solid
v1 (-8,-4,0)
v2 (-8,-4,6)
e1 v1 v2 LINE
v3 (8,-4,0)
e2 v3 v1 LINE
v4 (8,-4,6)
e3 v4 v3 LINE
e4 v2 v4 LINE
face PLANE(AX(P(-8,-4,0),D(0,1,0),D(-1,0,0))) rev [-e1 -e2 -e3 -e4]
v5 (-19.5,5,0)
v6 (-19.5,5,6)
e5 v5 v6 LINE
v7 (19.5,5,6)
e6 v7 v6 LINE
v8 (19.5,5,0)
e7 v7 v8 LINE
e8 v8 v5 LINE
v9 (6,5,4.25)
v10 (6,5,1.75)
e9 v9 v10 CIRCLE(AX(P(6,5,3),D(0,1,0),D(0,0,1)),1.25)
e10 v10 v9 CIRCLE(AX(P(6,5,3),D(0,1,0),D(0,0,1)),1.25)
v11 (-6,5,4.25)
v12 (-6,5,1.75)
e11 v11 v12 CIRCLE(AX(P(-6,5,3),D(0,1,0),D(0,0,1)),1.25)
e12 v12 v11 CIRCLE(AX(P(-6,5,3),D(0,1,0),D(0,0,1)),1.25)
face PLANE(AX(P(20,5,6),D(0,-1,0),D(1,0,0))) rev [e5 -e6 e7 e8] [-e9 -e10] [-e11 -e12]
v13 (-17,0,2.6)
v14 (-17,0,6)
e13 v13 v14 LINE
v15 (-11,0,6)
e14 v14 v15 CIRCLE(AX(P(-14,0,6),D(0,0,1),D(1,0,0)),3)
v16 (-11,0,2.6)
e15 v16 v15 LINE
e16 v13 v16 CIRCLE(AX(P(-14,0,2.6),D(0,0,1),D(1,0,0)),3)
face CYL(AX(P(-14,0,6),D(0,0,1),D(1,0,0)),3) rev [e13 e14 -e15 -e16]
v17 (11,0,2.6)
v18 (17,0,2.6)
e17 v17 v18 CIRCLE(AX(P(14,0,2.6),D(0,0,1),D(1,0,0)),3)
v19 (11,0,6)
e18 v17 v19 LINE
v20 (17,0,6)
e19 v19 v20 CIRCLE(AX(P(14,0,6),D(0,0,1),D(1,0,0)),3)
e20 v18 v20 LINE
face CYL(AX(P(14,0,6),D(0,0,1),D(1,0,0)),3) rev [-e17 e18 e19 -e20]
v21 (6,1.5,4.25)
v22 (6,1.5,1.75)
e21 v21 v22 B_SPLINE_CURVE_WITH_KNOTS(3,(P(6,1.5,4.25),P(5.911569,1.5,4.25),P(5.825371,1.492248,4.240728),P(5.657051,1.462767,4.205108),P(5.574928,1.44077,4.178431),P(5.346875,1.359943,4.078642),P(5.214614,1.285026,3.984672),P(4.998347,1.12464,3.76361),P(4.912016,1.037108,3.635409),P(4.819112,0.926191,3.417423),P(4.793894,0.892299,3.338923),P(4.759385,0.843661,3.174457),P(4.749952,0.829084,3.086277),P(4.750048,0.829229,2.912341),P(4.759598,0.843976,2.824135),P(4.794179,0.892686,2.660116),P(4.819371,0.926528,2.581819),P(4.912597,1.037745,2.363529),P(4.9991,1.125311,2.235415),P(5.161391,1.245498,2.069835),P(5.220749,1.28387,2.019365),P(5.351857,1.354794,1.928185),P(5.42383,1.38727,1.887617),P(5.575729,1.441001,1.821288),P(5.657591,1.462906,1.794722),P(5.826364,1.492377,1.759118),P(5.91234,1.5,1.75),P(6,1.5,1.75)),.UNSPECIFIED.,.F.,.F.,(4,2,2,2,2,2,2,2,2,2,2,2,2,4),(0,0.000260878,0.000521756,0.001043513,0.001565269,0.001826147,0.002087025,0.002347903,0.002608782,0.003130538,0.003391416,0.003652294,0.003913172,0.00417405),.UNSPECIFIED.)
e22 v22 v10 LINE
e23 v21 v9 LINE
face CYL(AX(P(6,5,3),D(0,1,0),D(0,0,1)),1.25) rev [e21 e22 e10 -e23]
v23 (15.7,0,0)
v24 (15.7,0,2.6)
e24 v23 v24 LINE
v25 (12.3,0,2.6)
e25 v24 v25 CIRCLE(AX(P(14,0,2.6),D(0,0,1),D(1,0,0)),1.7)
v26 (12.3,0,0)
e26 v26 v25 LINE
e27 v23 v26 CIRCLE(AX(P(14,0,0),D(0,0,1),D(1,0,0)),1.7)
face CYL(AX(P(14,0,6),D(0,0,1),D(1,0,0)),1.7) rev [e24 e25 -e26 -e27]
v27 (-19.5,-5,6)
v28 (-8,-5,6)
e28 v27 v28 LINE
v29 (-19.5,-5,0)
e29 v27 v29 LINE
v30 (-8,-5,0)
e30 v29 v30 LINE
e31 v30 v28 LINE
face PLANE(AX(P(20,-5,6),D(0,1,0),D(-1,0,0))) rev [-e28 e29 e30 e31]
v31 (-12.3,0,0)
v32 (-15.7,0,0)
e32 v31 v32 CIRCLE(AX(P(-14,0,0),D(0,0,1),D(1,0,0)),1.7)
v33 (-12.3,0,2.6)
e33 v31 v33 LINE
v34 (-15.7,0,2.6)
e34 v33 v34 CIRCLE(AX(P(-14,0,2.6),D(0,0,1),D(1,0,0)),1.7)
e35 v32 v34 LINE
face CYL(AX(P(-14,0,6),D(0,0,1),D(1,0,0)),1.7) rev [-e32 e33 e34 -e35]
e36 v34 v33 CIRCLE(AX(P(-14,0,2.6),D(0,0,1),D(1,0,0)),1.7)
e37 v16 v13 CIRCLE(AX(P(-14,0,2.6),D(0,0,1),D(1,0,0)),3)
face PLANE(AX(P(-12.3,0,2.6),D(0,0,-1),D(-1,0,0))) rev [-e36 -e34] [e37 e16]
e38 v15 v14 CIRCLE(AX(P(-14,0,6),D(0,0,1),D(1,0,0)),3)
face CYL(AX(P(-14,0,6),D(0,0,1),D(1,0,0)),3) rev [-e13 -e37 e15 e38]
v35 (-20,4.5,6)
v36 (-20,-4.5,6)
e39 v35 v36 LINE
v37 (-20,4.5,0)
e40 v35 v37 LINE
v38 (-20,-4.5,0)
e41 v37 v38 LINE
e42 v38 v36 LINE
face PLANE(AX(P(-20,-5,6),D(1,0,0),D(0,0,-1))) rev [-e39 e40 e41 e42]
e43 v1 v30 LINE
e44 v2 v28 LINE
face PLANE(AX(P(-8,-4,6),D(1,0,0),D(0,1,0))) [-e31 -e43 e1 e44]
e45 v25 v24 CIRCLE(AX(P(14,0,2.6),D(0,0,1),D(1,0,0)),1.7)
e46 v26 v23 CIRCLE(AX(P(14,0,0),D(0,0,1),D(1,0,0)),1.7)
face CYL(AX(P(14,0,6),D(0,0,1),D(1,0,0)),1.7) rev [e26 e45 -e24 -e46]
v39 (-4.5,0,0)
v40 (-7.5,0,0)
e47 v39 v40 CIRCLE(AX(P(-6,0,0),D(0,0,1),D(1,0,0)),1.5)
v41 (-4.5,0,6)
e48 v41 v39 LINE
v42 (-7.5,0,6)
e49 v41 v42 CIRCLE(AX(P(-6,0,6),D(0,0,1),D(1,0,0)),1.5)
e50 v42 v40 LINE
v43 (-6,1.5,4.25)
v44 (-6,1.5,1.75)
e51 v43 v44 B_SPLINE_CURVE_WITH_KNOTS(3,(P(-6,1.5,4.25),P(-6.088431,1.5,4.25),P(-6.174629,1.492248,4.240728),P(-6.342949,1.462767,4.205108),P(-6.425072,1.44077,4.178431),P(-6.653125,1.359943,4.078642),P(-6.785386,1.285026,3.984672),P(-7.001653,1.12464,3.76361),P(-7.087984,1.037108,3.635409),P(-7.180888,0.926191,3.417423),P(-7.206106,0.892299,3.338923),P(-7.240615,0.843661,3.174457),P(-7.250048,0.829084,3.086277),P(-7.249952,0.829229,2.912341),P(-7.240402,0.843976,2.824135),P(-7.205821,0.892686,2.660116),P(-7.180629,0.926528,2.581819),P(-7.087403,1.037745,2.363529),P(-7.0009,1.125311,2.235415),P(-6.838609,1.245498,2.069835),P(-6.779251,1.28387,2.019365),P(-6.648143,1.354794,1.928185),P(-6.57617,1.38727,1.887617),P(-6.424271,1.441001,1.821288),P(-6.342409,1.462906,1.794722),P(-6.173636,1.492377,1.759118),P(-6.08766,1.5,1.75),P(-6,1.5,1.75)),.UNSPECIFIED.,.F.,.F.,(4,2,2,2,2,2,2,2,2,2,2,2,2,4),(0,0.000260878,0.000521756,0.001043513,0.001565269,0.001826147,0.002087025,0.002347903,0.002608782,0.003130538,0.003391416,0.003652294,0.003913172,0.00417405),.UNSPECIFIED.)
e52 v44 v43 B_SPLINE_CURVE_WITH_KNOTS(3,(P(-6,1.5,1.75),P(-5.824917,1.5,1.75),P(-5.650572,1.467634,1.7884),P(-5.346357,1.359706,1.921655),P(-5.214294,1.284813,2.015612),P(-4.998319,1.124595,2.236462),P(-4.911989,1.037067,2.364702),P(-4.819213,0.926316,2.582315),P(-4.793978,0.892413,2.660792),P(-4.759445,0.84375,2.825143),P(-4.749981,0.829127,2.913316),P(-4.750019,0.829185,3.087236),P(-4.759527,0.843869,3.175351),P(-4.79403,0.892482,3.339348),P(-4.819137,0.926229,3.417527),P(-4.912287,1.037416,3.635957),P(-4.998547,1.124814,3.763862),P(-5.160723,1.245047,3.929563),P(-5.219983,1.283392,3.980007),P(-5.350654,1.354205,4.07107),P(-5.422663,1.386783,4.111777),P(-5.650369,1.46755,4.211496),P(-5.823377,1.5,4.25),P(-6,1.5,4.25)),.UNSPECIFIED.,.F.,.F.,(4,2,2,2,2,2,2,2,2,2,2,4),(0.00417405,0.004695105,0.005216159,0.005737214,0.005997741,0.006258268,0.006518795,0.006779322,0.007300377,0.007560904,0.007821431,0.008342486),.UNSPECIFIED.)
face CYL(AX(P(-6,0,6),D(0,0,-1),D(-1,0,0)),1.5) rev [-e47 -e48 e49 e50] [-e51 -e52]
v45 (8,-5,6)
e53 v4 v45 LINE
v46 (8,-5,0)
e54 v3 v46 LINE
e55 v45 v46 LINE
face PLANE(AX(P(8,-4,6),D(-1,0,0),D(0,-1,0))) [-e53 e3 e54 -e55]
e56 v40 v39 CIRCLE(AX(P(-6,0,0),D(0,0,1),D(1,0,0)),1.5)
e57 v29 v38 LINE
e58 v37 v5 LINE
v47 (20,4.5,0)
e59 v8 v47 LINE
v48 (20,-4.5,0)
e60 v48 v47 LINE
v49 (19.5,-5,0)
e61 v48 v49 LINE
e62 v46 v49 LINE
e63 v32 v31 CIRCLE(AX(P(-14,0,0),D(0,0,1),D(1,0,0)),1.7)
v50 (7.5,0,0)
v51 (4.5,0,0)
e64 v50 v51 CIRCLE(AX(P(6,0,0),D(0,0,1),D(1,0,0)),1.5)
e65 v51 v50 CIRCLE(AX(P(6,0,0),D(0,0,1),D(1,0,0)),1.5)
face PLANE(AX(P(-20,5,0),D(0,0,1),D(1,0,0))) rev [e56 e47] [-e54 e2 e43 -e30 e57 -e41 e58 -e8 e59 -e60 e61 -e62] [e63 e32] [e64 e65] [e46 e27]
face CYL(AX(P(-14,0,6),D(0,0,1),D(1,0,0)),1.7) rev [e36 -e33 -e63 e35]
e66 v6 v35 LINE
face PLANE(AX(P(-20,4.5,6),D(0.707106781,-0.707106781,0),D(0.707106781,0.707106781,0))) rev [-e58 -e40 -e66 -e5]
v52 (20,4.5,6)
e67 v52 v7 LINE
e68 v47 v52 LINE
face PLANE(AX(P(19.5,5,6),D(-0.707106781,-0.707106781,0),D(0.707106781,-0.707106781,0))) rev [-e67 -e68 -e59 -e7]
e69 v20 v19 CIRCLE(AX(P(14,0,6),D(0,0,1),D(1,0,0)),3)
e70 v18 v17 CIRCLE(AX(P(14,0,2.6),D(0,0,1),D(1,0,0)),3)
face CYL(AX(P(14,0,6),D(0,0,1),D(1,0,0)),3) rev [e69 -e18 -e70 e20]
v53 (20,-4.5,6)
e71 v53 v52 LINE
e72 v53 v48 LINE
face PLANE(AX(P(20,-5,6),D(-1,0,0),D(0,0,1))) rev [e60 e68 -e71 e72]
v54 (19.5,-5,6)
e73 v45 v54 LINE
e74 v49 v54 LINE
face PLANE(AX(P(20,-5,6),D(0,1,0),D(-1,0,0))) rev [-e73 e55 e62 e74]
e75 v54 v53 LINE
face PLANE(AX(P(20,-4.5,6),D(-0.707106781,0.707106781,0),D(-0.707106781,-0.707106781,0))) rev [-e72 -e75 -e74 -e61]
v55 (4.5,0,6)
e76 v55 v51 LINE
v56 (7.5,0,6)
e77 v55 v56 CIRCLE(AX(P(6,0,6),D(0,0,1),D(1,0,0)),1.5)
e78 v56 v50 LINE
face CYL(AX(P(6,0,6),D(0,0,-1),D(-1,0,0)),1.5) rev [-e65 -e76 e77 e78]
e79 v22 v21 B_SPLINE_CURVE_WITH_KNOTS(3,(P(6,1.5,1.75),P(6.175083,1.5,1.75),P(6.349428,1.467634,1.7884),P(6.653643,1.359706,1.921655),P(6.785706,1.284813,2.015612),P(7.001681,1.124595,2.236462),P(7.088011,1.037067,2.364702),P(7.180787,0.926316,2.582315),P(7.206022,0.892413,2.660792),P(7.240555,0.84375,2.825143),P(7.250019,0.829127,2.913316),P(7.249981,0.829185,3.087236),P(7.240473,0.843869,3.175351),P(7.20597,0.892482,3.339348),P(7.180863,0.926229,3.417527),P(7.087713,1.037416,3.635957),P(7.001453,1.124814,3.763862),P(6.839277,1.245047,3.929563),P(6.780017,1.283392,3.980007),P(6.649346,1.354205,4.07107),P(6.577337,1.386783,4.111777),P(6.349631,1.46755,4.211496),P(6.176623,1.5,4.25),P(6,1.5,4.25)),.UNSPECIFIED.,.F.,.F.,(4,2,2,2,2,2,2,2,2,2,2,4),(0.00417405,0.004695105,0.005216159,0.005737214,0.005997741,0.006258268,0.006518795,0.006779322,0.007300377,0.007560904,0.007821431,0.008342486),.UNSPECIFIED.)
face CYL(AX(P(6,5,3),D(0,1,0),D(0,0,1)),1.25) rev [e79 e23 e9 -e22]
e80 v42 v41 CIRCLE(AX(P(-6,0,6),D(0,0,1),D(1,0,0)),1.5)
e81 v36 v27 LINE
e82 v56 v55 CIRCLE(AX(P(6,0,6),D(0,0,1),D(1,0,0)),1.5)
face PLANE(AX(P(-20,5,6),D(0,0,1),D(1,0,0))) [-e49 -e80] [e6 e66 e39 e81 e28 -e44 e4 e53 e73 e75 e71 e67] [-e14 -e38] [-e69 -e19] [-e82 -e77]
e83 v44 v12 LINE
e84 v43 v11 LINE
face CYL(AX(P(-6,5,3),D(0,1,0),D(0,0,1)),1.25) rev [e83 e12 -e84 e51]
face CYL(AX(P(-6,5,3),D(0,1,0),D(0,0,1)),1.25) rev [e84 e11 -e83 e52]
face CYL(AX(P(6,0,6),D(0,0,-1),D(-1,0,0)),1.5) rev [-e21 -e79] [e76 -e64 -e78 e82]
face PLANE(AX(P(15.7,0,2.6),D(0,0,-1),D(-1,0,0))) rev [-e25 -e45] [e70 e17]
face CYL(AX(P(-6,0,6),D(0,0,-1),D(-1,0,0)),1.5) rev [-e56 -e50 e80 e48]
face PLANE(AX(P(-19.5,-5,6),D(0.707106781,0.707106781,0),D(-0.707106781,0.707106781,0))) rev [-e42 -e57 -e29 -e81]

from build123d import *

# Parameters (mm, degrees)
SKETCH1_W                                            = 40
SKETCH1_H                                            = 10
BOSS_EXTRUDE1_DEPTH                                  = 6
CHAMFER1_SIZE                                        = 0.5
HOLE_SIZE_PER_SOCKET_HEAD_CAP_SCREW_TYPE_D           = 3.4
HOLE_SIZE_PER_SOCKET_HEAD_CAP_SCREW_TYPE_CBORE_D     = 6
HOLE_SIZE_PER_SOCKET_HEAD_CAP_SCREW_TYPE_CBORE_DEPTH = 3.4
SKETCH4_W                                            = 16
SKETCH4_H                                            = 6
CUT_EXTRUDE1_DEPTH                                   = 1
SKETCH5_R                                            = 1.5
CUT_EXTRUDE2_DEPTH                                   = 22.470910554
M3_TAPPED_HOLE1_D                                    = 2.5
M3_TAPPED_HOLE1_DEPTH                                = 5
M3_TAPPED_HOLE1_TIP                                  = 0.751075774


with BuildPart() as part:
    # Sketch1 → Boss-Extrude1 (new body)
    with BuildSketch(Plane.XY):
        Rectangle(SKETCH1_W, SKETCH1_H)
    extrude(amount=BOSS_EXTRUDE1_DEPTH)

    # Chamfer1
    chamfer1_edges = [part.edges().sort_by_distance(p)[0] for p in [
        (-20, 5, 3),
        (20, 5, 3),
        (20, -5, 3),
        (-20, -5, 3),
    ]]
    chamfer(chamfer1_edges, length=CHAMFER1_SIZE)

    # Hole Size per Socket Head Cap Screw Type1 (through all)
    with Locations(Plane.XY.offset(6)):
        with Locations((-14, 0), (14, 0)):
            CounterBoreHole(HOLE_SIZE_PER_SOCKET_HEAD_CAP_SCREW_TYPE_D / 2, HOLE_SIZE_PER_SOCKET_HEAD_CAP_SCREW_TYPE_CBORE_D / 2, HOLE_SIZE_PER_SOCKET_HEAD_CAP_SCREW_TYPE_CBORE_DEPTH)

    # Sketch4 → Cut-Extrude1 (cut)
    with BuildSketch(Plane(origin=(0, -5, 0), x_dir=(1, 0, 0), z_dir=(0, 1, 0))):
        with Locations((0, -3)):
            Rectangle(SKETCH4_W, SKETCH4_H)
    extrude(amount=CUT_EXTRUDE1_DEPTH, mode=Mode.SUBTRACT)

    # Sketch5 → Cut-Extrude2 (cut, through all)
    with BuildSketch(Plane.XY):
        with Locations((-6, 0)):
            Circle(SKETCH5_R)
        with Locations((6, 0)):
            Circle(SKETCH5_R)
    extrude(amount=CUT_EXTRUDE2_DEPTH, mode=Mode.SUBTRACT)

    # M3 Tapped Hole1
    with Locations(Plane(origin=(0, 5, 0), x_dir=(-1, 0, 0), z_dir=(0, 1, 0))):
        with Locations((6, 3), (-6, 3)):
            Hole(M3_TAPPED_HOLE1_D / 2, depth=M3_TAPPED_HOLE1_DEPTH)
            with Locations((0, 0, -(M3_TAPPED_HOLE1_DEPTH + M3_TAPPED_HOLE1_TIP / 2))):  # 118° drill point
                Cone(0, M3_TAPPED_HOLE1_D / 2, M3_TAPPED_HOLE1_TIP, mode=Mode.SUBTRACT)


solid = part.part
